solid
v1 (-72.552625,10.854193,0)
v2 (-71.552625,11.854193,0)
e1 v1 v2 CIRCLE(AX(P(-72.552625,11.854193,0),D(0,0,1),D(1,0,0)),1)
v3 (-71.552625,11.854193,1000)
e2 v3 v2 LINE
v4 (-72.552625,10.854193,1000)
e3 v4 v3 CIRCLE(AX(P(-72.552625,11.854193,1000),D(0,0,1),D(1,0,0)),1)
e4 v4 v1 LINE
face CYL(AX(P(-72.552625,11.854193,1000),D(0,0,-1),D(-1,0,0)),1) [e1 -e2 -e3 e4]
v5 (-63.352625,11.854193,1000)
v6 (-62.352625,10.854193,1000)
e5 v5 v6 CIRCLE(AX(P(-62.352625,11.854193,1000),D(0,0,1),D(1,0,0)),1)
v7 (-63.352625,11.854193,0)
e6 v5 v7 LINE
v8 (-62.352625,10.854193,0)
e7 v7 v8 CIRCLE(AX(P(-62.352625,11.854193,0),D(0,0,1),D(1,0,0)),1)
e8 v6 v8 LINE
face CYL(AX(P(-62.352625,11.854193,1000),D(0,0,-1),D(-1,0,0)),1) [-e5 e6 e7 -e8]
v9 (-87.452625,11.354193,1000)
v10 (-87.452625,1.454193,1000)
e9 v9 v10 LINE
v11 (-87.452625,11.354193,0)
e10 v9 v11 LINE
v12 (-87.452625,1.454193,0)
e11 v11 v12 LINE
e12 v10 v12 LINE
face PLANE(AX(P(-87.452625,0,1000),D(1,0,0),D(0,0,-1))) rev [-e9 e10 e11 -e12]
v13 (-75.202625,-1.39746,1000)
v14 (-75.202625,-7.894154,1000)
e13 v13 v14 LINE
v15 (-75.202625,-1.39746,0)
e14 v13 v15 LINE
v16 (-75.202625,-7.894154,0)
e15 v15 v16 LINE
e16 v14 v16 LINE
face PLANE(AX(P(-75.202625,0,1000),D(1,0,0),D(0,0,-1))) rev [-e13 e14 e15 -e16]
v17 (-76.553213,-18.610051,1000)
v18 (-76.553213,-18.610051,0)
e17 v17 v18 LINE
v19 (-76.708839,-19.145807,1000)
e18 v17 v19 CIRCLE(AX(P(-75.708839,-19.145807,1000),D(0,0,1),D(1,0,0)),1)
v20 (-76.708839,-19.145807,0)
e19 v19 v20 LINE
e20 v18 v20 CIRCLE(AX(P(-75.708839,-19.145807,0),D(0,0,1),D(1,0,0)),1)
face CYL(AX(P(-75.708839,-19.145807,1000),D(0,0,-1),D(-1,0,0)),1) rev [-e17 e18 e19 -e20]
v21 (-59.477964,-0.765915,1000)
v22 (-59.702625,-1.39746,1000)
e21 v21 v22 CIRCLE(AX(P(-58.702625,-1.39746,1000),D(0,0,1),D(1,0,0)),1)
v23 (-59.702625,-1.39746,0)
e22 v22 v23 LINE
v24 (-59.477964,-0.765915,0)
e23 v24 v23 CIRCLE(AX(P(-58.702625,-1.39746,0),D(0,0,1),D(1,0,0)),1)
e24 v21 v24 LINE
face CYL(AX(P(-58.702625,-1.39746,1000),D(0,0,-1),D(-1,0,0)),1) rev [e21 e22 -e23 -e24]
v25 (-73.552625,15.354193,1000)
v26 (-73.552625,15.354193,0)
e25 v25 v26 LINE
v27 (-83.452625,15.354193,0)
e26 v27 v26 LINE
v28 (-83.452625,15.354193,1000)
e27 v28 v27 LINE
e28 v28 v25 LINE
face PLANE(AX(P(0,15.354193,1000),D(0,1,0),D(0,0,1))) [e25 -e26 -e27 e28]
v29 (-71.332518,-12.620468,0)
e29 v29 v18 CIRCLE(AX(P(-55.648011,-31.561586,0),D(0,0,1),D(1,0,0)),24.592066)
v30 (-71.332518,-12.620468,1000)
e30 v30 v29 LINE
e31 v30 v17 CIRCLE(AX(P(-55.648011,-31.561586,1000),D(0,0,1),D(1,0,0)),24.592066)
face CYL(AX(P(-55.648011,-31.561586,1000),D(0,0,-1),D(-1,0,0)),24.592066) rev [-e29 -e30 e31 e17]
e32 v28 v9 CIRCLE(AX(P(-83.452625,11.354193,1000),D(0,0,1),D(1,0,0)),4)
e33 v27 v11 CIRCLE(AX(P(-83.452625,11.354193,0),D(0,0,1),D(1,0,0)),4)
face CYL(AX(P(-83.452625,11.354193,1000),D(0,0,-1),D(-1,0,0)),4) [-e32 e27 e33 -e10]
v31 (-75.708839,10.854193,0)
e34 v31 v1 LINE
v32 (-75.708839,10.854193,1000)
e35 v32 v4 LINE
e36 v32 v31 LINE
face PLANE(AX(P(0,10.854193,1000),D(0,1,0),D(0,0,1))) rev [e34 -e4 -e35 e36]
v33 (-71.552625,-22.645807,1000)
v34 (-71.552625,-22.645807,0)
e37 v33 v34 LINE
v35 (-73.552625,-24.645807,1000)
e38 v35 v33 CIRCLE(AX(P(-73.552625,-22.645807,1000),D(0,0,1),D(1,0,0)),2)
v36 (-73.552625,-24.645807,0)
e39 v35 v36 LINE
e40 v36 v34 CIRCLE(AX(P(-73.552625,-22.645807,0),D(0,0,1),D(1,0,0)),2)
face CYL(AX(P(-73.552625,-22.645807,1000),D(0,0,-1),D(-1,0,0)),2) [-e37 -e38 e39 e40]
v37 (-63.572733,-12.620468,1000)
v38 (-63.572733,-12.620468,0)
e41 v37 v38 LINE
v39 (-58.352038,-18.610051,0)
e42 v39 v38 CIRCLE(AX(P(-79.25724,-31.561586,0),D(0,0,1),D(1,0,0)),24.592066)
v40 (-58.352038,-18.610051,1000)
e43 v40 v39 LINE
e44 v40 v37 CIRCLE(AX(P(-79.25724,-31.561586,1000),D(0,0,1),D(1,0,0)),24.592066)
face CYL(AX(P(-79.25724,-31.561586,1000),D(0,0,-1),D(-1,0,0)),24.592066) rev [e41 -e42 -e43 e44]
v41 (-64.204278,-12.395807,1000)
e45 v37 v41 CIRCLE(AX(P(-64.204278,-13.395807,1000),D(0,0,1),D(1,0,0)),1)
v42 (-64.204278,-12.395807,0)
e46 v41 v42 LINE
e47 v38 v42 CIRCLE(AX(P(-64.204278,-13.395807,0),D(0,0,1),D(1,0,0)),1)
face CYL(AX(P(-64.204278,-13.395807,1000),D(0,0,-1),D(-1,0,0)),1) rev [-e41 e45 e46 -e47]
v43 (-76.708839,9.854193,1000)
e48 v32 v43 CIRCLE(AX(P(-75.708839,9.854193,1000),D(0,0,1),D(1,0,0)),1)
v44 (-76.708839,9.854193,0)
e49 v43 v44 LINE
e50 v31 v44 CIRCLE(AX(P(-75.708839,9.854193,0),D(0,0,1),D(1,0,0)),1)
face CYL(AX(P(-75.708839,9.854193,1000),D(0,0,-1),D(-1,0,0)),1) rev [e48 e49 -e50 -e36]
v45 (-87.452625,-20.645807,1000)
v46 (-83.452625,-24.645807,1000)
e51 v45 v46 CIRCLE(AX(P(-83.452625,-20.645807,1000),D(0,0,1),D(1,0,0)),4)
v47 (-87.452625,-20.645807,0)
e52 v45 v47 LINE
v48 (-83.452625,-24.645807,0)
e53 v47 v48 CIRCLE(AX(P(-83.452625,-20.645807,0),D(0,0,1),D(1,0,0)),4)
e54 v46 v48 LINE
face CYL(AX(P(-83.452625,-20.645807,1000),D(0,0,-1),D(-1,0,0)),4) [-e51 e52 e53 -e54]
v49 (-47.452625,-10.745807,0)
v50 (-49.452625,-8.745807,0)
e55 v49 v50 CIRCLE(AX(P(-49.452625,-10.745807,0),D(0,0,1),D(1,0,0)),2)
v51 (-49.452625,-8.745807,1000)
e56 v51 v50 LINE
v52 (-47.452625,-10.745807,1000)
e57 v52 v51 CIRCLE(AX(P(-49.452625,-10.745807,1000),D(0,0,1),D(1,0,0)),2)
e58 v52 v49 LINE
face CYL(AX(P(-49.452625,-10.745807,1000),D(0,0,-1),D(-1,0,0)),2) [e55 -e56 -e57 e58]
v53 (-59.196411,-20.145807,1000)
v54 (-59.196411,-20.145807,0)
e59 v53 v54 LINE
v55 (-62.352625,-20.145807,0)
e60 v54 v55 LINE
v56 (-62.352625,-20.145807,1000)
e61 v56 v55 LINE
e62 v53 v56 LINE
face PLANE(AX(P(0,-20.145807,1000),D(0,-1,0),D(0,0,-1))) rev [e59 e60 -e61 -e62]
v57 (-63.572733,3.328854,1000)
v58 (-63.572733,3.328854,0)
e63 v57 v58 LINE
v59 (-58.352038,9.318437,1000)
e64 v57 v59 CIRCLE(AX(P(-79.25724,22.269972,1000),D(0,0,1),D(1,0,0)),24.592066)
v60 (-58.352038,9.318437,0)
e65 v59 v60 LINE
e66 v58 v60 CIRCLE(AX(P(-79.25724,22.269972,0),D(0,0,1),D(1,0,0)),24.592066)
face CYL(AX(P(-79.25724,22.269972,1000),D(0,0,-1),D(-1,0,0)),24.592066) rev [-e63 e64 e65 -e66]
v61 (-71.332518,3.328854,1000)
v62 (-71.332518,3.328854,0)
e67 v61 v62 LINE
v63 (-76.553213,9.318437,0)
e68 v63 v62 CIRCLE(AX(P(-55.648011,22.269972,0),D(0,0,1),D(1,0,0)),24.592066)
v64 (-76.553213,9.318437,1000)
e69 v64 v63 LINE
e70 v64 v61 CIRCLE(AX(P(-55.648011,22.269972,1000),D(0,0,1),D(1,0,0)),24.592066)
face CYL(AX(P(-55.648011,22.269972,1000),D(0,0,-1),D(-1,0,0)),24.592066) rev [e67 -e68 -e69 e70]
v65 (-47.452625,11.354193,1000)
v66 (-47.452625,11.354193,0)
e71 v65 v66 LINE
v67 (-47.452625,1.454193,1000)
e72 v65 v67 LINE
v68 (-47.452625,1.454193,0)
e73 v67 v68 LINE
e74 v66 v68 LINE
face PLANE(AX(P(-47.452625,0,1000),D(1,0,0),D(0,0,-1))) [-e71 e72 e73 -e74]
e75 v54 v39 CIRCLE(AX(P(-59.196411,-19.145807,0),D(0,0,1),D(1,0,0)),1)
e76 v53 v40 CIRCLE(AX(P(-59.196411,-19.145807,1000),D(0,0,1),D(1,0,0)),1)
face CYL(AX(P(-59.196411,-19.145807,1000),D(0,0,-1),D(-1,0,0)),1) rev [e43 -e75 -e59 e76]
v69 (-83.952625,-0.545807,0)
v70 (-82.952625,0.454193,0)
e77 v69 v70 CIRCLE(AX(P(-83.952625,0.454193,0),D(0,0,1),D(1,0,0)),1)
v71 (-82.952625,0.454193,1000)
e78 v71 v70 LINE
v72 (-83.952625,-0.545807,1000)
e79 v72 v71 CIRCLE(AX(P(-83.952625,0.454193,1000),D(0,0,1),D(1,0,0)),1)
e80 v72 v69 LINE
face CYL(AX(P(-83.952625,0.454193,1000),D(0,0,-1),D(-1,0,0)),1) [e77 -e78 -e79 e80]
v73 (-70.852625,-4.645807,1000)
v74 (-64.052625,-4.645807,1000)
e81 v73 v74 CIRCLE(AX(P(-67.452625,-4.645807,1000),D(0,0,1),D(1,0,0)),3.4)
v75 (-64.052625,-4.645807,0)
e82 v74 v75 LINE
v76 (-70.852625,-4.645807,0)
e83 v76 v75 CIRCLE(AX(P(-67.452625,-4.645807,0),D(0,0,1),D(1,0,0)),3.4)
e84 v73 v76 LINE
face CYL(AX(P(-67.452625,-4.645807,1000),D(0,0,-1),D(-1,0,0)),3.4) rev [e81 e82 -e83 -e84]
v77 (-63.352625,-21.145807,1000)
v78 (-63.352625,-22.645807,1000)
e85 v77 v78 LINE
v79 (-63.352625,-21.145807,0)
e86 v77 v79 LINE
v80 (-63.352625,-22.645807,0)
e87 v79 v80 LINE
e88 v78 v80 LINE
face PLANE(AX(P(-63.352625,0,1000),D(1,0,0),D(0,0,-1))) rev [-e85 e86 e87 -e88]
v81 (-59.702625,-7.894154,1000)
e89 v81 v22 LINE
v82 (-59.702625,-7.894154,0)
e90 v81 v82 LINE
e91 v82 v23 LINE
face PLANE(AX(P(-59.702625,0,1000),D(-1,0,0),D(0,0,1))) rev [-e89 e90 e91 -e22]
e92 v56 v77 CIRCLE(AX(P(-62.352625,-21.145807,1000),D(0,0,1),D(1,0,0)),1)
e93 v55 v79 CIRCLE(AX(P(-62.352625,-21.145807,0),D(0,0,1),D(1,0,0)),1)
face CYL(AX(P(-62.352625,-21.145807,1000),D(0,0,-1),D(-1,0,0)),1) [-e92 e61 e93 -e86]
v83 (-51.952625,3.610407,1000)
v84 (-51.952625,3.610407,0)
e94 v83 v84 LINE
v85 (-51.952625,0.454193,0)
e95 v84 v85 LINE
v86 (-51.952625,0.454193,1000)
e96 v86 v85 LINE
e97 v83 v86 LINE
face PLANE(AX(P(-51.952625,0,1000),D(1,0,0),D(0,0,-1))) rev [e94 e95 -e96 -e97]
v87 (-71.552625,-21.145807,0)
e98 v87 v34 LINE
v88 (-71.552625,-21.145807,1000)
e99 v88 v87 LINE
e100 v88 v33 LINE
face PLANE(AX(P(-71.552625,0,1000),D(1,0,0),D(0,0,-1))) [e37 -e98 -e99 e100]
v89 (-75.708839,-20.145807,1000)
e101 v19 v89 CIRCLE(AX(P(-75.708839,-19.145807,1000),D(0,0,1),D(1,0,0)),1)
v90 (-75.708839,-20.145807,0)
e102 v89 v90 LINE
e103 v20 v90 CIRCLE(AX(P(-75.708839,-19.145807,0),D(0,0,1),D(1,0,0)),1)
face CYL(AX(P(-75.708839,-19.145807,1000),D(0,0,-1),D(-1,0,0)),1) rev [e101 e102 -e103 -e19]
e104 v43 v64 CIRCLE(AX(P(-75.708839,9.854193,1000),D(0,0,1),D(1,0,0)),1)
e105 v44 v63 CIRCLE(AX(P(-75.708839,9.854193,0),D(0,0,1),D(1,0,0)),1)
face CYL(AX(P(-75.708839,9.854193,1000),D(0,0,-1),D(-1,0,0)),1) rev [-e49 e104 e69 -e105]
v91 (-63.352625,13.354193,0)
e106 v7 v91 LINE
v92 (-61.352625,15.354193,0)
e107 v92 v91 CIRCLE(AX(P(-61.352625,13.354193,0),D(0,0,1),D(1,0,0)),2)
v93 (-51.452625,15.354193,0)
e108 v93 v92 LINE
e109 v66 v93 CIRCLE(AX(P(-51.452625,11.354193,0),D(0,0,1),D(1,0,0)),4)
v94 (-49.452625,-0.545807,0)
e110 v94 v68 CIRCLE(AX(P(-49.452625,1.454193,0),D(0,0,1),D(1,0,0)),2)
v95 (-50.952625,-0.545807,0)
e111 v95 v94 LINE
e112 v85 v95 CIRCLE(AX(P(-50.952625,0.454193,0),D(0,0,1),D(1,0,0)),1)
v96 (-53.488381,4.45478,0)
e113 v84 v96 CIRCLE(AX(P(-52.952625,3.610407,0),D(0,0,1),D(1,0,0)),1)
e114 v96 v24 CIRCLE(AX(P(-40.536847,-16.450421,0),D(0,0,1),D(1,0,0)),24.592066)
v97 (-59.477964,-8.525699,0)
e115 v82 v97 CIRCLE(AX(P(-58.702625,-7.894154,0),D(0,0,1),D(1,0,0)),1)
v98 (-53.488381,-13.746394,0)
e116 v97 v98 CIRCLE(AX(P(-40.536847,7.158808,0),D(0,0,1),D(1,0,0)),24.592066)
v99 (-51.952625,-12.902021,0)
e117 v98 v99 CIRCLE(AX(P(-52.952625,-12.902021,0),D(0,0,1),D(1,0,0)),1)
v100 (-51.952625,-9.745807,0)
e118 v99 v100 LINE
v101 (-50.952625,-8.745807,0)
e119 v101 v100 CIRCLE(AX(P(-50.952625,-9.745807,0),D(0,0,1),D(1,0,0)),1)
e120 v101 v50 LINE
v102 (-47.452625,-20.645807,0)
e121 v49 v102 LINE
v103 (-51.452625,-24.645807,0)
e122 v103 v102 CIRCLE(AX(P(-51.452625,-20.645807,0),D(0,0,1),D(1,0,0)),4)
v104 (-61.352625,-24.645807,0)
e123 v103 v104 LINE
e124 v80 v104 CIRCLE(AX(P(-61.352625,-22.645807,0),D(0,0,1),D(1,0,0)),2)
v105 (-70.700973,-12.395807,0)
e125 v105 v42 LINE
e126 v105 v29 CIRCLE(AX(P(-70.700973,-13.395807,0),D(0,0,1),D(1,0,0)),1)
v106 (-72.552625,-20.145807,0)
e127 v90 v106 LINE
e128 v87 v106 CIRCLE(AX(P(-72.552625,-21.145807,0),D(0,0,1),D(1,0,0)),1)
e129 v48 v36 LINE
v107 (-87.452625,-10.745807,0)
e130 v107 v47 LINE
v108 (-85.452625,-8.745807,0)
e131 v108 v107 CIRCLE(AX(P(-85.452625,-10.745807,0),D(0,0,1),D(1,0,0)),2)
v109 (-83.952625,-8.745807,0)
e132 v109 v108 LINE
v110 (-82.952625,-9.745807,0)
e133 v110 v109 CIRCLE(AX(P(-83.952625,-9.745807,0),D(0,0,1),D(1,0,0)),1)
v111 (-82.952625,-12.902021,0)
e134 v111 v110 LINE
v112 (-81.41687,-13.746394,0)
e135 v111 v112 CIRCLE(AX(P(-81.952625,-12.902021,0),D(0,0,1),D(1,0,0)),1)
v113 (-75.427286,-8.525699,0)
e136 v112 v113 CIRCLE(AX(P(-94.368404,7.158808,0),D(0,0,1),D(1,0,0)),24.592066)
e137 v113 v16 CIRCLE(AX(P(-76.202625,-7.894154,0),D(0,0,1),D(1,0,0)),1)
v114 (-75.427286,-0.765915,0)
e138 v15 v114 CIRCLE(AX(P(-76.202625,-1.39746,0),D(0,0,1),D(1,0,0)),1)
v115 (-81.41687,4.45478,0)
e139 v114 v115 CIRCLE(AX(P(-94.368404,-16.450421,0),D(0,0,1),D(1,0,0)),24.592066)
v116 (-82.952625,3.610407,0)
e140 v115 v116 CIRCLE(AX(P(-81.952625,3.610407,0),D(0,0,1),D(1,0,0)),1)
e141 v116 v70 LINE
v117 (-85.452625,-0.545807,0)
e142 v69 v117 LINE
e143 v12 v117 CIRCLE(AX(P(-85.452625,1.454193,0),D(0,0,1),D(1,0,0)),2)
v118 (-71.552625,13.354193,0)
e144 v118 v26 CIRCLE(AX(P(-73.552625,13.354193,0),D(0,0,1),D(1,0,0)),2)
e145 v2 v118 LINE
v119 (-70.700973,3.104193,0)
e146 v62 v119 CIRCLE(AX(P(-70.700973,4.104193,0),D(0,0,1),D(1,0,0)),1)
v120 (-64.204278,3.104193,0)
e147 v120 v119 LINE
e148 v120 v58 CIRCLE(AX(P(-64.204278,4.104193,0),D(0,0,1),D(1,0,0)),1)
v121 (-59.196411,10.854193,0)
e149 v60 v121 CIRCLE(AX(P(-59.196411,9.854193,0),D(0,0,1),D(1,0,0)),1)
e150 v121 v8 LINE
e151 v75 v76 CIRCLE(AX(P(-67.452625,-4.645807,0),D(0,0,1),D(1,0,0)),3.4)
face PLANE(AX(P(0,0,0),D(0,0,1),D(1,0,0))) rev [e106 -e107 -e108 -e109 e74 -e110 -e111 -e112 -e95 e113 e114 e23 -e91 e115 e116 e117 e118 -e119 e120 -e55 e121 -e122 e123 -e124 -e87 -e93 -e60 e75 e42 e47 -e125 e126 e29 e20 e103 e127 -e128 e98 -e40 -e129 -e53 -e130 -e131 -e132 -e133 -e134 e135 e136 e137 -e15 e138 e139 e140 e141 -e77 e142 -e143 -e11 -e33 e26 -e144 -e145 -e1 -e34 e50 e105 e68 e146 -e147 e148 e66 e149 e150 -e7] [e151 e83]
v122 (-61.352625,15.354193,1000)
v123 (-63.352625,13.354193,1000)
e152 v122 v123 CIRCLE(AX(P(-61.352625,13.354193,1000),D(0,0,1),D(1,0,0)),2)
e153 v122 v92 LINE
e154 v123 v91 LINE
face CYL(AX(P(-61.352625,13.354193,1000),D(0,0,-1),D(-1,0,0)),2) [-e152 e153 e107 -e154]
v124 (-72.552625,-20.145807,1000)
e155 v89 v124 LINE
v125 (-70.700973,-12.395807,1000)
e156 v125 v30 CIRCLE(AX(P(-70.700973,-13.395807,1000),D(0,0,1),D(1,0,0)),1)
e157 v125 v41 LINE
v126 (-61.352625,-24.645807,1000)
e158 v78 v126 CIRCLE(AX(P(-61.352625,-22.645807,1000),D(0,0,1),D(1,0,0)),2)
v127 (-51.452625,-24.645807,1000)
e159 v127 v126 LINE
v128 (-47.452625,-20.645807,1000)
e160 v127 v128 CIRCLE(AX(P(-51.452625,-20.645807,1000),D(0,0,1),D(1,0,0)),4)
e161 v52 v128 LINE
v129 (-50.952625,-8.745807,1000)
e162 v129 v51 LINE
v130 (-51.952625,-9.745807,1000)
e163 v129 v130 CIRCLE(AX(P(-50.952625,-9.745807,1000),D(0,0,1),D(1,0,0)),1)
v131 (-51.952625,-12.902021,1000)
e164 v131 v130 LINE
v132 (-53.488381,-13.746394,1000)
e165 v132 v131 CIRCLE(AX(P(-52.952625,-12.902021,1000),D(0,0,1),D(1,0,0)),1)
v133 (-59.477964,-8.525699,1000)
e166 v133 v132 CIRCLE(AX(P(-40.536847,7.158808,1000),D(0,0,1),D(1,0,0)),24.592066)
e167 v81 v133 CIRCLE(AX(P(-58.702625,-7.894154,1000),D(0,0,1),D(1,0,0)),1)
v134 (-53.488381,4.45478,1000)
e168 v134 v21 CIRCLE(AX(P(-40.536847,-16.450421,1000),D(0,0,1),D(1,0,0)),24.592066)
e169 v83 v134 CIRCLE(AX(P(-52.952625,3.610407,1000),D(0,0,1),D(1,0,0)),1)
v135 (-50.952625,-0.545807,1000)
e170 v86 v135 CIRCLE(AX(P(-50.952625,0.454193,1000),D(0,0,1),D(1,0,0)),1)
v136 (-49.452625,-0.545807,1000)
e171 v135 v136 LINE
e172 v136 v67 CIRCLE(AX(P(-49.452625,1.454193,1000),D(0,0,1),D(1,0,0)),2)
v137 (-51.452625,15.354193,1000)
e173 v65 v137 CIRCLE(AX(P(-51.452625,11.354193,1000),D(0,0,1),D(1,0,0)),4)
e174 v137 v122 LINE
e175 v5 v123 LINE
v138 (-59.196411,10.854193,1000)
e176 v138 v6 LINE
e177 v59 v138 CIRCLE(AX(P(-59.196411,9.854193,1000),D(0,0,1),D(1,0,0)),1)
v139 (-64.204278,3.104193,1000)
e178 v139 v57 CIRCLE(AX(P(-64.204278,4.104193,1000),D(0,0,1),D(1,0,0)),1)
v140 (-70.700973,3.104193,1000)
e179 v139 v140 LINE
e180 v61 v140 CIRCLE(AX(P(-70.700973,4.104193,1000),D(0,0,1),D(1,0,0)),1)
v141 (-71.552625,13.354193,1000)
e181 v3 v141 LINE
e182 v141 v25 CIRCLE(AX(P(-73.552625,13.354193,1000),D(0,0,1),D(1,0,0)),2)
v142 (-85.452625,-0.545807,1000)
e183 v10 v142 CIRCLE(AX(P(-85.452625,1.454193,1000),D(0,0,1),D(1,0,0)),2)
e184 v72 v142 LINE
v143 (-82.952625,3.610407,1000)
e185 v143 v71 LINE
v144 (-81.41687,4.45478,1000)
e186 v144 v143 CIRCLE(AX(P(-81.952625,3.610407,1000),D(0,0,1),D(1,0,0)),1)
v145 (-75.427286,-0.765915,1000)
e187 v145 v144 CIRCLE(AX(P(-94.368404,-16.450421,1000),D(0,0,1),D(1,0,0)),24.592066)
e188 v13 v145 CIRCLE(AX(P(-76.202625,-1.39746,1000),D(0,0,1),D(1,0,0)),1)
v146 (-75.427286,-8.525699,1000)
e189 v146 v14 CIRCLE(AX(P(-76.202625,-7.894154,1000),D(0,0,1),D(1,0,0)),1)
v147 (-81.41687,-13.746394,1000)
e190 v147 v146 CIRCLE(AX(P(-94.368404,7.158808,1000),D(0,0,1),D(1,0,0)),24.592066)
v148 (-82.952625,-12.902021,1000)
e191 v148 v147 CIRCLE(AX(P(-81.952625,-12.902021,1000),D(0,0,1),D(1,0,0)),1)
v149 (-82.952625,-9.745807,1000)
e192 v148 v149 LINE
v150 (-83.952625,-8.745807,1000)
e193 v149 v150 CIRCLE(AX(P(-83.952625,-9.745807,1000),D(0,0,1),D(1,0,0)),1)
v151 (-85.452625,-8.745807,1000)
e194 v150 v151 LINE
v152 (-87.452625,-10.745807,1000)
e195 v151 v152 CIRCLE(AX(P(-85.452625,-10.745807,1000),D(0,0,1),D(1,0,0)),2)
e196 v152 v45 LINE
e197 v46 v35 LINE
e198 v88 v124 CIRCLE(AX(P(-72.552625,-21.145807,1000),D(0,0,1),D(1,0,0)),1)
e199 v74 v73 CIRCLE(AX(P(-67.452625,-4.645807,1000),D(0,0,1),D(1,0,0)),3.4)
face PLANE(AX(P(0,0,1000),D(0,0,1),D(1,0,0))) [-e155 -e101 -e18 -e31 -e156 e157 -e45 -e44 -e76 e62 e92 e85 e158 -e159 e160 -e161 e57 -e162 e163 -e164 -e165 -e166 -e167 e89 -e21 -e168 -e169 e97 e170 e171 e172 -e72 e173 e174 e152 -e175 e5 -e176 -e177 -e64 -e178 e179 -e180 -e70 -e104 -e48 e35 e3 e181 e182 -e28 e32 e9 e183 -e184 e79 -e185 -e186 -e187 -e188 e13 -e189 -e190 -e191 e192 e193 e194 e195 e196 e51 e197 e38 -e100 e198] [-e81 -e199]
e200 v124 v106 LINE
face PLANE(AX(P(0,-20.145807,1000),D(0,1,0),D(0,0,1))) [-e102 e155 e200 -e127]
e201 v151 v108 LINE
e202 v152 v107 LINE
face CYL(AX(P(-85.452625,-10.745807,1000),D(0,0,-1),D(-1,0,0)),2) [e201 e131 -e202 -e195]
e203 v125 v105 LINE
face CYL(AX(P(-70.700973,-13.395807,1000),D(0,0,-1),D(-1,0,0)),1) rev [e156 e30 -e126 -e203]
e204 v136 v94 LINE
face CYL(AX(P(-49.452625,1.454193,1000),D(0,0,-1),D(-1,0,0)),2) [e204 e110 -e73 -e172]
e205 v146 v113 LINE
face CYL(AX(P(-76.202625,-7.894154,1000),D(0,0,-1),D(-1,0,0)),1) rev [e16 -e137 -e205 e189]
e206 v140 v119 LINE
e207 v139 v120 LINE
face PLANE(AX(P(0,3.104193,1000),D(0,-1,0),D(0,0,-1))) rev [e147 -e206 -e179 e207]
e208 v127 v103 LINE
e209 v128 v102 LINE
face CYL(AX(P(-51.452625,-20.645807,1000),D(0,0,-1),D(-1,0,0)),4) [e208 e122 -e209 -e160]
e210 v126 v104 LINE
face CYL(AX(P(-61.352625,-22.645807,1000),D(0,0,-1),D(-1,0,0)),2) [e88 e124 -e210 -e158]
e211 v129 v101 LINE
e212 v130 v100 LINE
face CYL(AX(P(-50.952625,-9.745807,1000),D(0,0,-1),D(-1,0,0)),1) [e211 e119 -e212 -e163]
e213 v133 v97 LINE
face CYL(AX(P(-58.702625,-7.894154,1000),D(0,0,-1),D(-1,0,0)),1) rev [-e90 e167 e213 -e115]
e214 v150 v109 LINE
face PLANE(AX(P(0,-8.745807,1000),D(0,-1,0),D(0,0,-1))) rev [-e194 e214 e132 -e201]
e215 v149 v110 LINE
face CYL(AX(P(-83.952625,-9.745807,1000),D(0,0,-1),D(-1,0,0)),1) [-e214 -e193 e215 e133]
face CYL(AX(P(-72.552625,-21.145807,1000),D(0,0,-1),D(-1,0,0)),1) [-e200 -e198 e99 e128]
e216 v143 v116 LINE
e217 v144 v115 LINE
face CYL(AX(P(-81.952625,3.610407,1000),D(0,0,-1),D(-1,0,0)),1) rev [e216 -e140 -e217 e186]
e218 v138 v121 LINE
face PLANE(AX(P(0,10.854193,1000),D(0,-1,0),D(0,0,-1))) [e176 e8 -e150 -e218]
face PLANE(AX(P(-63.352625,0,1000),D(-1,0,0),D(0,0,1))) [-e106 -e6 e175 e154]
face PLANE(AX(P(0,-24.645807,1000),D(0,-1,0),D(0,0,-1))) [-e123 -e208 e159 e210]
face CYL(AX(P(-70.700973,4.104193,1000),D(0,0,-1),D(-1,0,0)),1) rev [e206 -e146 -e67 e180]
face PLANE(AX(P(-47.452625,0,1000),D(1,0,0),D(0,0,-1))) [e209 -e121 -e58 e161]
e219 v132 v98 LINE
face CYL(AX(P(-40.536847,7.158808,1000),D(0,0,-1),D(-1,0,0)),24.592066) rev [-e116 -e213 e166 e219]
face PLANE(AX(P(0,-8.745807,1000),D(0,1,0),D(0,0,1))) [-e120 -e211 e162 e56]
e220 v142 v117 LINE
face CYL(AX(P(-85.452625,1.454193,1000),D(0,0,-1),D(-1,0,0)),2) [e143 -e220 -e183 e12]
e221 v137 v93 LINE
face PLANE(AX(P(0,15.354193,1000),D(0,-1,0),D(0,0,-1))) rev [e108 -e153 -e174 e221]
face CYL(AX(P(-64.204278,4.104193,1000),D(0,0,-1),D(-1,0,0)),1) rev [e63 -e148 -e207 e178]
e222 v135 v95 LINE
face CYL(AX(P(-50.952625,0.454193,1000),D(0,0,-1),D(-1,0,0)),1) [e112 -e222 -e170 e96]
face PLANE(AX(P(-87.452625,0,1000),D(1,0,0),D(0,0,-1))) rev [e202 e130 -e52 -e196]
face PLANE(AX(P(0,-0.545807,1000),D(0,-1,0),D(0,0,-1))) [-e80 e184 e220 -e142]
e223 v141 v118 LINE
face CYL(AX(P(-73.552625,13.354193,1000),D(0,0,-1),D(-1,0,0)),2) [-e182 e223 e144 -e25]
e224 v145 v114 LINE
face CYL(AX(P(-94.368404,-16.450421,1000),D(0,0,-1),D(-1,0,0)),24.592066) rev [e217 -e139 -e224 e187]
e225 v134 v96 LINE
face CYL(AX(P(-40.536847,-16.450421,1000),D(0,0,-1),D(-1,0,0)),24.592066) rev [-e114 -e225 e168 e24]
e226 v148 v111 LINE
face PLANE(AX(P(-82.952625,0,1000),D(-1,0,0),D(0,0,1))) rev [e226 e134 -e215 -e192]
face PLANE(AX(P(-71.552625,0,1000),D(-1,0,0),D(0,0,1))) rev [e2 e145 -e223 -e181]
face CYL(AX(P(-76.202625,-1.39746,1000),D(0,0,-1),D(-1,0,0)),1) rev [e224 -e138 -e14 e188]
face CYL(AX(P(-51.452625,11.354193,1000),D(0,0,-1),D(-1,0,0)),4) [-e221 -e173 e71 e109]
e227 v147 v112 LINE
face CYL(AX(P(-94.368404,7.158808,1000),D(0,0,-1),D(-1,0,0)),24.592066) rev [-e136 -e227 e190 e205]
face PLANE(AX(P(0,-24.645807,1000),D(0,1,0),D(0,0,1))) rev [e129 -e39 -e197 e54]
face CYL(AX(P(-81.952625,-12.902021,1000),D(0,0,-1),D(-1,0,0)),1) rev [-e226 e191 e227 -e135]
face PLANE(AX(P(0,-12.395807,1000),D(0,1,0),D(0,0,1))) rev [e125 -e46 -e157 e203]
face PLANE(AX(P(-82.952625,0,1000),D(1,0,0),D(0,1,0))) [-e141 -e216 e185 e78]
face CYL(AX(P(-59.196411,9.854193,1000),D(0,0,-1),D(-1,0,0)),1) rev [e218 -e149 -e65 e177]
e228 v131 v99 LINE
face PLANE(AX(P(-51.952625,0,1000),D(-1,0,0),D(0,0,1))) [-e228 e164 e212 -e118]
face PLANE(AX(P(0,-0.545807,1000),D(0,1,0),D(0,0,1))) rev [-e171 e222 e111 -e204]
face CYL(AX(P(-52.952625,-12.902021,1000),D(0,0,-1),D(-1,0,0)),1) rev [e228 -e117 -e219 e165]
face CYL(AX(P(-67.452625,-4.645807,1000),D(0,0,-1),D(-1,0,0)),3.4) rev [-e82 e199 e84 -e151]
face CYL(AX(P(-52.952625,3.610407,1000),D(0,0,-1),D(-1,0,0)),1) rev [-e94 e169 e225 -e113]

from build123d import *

# Parameters (mm, degrees)
SKETCH1_R           = 3.4
BOSS_EXTRUDE1_DEPTH = 1000


with BuildPart() as part:
    # Sketch1 → Boss-Extrude1 (new body)
    with BuildSketch(Plane.XY):
        with BuildLine():
            Line((-72.552625451, -20.1458069), (-75.708839475, -20.1458069))
            ThreePointArc((-75.708839475, -20.1458069), (-76.585125865, -19.62759748), (-76.55321253, -18.610051226))
            ThreePointArc((-76.55321253, -18.610051226), (-74.186362214, -15.403020453), (-71.332517782, -12.620467892))
            ThreePointArc((-71.332517782, -12.620467892), (-71.036129936, -12.453644757), (-70.700972516, -12.3958069))
            Line((-70.700972516, -12.3958069), (-67.452625451, -12.3958069))
            Line((-67.452625451, -12.3958069), (-64.204278386, -12.3958069))
            ThreePointArc((-64.204278386, -12.3958069), (-63.869120967, -12.453644757), (-63.572733121, -12.620467892))
            ThreePointArc((-63.572733121, -12.620467892), (-60.718888688, -15.403020453), (-58.352038372, -18.610051226))
            ThreePointArc((-58.352038372, -18.610051226), (-58.320125037, -19.62759748), (-59.196411427, -20.1458069))
            Line((-59.196411427, -20.1458069), (-62.352625451, -20.1458069))
            ThreePointArc((-62.352625451, -20.1458069), (-63.059732232, -20.438700119), (-63.352625451, -21.1458069))
            Line((-63.352625451, -21.1458069), (-63.352625451, -22.6458069))
            ThreePointArc((-63.352625451, -22.6458069), (-62.766839013, -24.060020463), (-61.352625451, -24.6458069))
            Line((-61.352625451, -24.6458069), (-51.452625451, -24.6458069))
            ThreePointArc((-51.452625451, -24.6458069), (-48.624198326, -23.474234025), (-47.452625451, -20.6458069))
            Line((-47.452625451, -20.6458069), (-47.452625451, -10.7458069))
            ThreePointArc((-47.452625451, -10.7458069), (-48.038411889, -9.331593338), (-49.452625451, -8.7458069))
            Line((-49.452625451, -8.7458069), (-50.952625451, -8.7458069))
            ThreePointArc((-50.952625451, -8.7458069), (-51.659732232, -9.038700119), (-51.952625451, -9.7458069))
            Line((-51.952625451, -9.7458069), (-51.952625451, -12.902020924))
            ThreePointArc((-51.952625451, -12.902020924), (-52.470834871, -13.778307314), (-53.488381126, -13.74639398))
            ThreePointArc((-53.488381126, -13.74639398), (-56.695411898, -11.379543663), (-59.477964459, -8.525699231))
            ThreePointArc((-59.477964459, -8.525699231), (-59.644787594, -8.229311385), (-59.702625451, -7.894153965))
            Line((-59.702625451, -7.894153965), (-59.702625451, -4.6458069))
            Line((-59.702625451, -4.6458069), (-59.702625451, -1.397459836))
            ThreePointArc((-59.702625451, -1.397459836), (-59.644787594, -1.062302416), (-59.477964459, -0.76591457))
            ThreePointArc((-59.477964459, -0.76591457), (-56.695411898, 2.087929862), (-53.488381126, 4.454780179))
            ThreePointArc((-53.488381126, 4.454780179), (-52.470834871, 4.486693513), (-51.952625451, 3.610407123))
            Line((-51.952625451, 3.610407123), (-51.952625451, 0.4541931))
            ThreePointArc((-51.952625451, 0.4541931), (-51.659732232, -0.252913682), (-50.952625451, -0.5458069))
            Line((-50.952625451, -0.5458069), (-49.452625451, -0.5458069))
            ThreePointArc((-49.452625451, -0.5458069), (-48.038411889, 0.039979537), (-47.452625451, 1.4541931))
            Line((-47.452625451, 1.4541931), (-47.452625451, 11.3541931))
            ThreePointArc((-47.452625451, 11.3541931), (-48.624198326, 14.182620224), (-51.452625451, 15.3541931))
            Line((-51.452625451, 15.3541931), (-61.352625451, 15.3541931))
            ThreePointArc((-61.352625451, 15.3541931), (-62.766839013, 14.768406662), (-63.352625451, 13.3541931))
            Line((-63.352625451, 13.3541931), (-63.352625451, 11.8541931))
            ThreePointArc((-63.352625451, 11.8541931), (-63.059732232, 11.147086318), (-62.352625451, 10.8541931))
            Line((-62.352625451, 10.8541931), (-59.196411427, 10.8541931))
            ThreePointArc((-59.196411427, 10.8541931), (-58.320125037, 10.335983679), (-58.352038372, 9.318437425))
            ThreePointArc((-58.352038372, 9.318437425), (-60.718888688, 6.111406652), (-63.572733121, 3.328854091))
            ThreePointArc((-63.572733121, 3.328854091), (-63.869120967, 3.162030956), (-64.204278386, 3.1041931))
            Line((-64.204278386, 3.1041931), (-67.452625451, 3.1041931))
            Line((-67.452625451, 3.1041931), (-70.700972516, 3.1041931))
            ThreePointArc((-70.700972516, 3.1041931), (-71.036129936, 3.162030956), (-71.332517782, 3.328854091))
            ThreePointArc((-71.332517782, 3.328854091), (-74.186362214, 6.111406652), (-76.55321253, 9.318437425))
            ThreePointArc((-76.55321253, 9.318437425), (-76.585125865, 10.335983679), (-75.708839475, 10.8541931))
            Line((-75.708839475, 10.8541931), (-72.552625451, 10.8541931))
            ThreePointArc((-72.552625451, 10.8541931), (-71.84551867, 11.147086318), (-71.552625451, 11.8541931))
            Line((-71.552625451, 11.8541931), (-71.552625451, 13.3541931))
            ThreePointArc((-71.552625451, 13.3541931), (-72.138411889, 14.768406662), (-73.552625451, 15.3541931))
            Line((-73.552625451, 15.3541931), (-83.452625451, 15.3541931))
            ThreePointArc((-83.452625451, 15.3541931), (-86.281052576, 14.182620224), (-87.452625451, 11.3541931))
            Line((-87.452625451, 11.3541931), (-87.452625451, 1.4541931))
            ThreePointArc((-87.452625451, 1.4541931), (-86.866839013, 0.039979537), (-85.452625451, -0.5458069))
            Line((-85.452625451, -0.5458069), (-83.952625451, -0.5458069))
            ThreePointArc((-83.952625451, -0.5458069), (-83.24551867, -0.252913682), (-82.952625451, 0.4541931))
            Line((-82.952625451, 0.4541931), (-82.952625451, 3.610407123))
            ThreePointArc((-82.952625451, 3.610407123), (-82.434416031, 4.486693513), (-81.416869776, 4.454780179))
            ThreePointArc((-81.416869776, 4.454780179), (-78.209839004, 2.087929862), (-75.427286443, -0.76591457))
            ThreePointArc((-75.427286443, -0.76591457), (-75.260463308, -1.062302416), (-75.202625451, -1.397459836))
            Line((-75.202625451, -1.397459836), (-75.202625451, -4.6458069))
            Line((-75.202625451, -4.6458069), (-75.202625451, -7.894153965))
            ThreePointArc((-75.202625451, -7.894153965), (-75.260463308, -8.229311385), (-75.427286443, -8.525699231))
            ThreePointArc((-75.427286443, -8.525699231), (-78.209839004, -11.379543663), (-81.416869776, -13.74639398))
            ThreePointArc((-81.416869776, -13.74639398), (-82.434416031, -13.778307314), (-82.952625451, -12.902020924))
            Line((-82.952625451, -12.902020924), (-82.952625451, -9.7458069))
            ThreePointArc((-82.952625451, -9.7458069), (-83.24551867, -9.038700119), (-83.952625451, -8.7458069))
            Line((-83.952625451, -8.7458069), (-85.452625451, -8.7458069))
            ThreePointArc((-85.452625451, -8.7458069), (-86.866839013, -9.331593338), (-87.452625451, -10.7458069))
            Line((-87.452625451, -10.7458069), (-87.452625451, -20.6458069))
            ThreePointArc((-87.452625451, -20.6458069), (-86.281052576, -23.474234025), (-83.452625451, -24.6458069))
            Line((-83.452625451, -24.6458069), (-73.552625451, -24.6458069))
            ThreePointArc((-73.552625451, -24.6458069), (-72.138411889, -24.060020463), (-71.552625451, -22.6458069))
            Line((-71.552625451, -22.6458069), (-71.552625451, -21.1458069))
            ThreePointArc((-71.552625451, -21.1458069), (-71.84551867, -20.438700119), (-72.552625451, -20.1458069))
        make_face()
        with Locations((-67.452625451, -4.6458069)):
            Circle(SKETCH1_R, mode=Mode.SUBTRACT)
    extrude(amount=BOSS_EXTRUDE1_DEPTH)


solid = part.part
